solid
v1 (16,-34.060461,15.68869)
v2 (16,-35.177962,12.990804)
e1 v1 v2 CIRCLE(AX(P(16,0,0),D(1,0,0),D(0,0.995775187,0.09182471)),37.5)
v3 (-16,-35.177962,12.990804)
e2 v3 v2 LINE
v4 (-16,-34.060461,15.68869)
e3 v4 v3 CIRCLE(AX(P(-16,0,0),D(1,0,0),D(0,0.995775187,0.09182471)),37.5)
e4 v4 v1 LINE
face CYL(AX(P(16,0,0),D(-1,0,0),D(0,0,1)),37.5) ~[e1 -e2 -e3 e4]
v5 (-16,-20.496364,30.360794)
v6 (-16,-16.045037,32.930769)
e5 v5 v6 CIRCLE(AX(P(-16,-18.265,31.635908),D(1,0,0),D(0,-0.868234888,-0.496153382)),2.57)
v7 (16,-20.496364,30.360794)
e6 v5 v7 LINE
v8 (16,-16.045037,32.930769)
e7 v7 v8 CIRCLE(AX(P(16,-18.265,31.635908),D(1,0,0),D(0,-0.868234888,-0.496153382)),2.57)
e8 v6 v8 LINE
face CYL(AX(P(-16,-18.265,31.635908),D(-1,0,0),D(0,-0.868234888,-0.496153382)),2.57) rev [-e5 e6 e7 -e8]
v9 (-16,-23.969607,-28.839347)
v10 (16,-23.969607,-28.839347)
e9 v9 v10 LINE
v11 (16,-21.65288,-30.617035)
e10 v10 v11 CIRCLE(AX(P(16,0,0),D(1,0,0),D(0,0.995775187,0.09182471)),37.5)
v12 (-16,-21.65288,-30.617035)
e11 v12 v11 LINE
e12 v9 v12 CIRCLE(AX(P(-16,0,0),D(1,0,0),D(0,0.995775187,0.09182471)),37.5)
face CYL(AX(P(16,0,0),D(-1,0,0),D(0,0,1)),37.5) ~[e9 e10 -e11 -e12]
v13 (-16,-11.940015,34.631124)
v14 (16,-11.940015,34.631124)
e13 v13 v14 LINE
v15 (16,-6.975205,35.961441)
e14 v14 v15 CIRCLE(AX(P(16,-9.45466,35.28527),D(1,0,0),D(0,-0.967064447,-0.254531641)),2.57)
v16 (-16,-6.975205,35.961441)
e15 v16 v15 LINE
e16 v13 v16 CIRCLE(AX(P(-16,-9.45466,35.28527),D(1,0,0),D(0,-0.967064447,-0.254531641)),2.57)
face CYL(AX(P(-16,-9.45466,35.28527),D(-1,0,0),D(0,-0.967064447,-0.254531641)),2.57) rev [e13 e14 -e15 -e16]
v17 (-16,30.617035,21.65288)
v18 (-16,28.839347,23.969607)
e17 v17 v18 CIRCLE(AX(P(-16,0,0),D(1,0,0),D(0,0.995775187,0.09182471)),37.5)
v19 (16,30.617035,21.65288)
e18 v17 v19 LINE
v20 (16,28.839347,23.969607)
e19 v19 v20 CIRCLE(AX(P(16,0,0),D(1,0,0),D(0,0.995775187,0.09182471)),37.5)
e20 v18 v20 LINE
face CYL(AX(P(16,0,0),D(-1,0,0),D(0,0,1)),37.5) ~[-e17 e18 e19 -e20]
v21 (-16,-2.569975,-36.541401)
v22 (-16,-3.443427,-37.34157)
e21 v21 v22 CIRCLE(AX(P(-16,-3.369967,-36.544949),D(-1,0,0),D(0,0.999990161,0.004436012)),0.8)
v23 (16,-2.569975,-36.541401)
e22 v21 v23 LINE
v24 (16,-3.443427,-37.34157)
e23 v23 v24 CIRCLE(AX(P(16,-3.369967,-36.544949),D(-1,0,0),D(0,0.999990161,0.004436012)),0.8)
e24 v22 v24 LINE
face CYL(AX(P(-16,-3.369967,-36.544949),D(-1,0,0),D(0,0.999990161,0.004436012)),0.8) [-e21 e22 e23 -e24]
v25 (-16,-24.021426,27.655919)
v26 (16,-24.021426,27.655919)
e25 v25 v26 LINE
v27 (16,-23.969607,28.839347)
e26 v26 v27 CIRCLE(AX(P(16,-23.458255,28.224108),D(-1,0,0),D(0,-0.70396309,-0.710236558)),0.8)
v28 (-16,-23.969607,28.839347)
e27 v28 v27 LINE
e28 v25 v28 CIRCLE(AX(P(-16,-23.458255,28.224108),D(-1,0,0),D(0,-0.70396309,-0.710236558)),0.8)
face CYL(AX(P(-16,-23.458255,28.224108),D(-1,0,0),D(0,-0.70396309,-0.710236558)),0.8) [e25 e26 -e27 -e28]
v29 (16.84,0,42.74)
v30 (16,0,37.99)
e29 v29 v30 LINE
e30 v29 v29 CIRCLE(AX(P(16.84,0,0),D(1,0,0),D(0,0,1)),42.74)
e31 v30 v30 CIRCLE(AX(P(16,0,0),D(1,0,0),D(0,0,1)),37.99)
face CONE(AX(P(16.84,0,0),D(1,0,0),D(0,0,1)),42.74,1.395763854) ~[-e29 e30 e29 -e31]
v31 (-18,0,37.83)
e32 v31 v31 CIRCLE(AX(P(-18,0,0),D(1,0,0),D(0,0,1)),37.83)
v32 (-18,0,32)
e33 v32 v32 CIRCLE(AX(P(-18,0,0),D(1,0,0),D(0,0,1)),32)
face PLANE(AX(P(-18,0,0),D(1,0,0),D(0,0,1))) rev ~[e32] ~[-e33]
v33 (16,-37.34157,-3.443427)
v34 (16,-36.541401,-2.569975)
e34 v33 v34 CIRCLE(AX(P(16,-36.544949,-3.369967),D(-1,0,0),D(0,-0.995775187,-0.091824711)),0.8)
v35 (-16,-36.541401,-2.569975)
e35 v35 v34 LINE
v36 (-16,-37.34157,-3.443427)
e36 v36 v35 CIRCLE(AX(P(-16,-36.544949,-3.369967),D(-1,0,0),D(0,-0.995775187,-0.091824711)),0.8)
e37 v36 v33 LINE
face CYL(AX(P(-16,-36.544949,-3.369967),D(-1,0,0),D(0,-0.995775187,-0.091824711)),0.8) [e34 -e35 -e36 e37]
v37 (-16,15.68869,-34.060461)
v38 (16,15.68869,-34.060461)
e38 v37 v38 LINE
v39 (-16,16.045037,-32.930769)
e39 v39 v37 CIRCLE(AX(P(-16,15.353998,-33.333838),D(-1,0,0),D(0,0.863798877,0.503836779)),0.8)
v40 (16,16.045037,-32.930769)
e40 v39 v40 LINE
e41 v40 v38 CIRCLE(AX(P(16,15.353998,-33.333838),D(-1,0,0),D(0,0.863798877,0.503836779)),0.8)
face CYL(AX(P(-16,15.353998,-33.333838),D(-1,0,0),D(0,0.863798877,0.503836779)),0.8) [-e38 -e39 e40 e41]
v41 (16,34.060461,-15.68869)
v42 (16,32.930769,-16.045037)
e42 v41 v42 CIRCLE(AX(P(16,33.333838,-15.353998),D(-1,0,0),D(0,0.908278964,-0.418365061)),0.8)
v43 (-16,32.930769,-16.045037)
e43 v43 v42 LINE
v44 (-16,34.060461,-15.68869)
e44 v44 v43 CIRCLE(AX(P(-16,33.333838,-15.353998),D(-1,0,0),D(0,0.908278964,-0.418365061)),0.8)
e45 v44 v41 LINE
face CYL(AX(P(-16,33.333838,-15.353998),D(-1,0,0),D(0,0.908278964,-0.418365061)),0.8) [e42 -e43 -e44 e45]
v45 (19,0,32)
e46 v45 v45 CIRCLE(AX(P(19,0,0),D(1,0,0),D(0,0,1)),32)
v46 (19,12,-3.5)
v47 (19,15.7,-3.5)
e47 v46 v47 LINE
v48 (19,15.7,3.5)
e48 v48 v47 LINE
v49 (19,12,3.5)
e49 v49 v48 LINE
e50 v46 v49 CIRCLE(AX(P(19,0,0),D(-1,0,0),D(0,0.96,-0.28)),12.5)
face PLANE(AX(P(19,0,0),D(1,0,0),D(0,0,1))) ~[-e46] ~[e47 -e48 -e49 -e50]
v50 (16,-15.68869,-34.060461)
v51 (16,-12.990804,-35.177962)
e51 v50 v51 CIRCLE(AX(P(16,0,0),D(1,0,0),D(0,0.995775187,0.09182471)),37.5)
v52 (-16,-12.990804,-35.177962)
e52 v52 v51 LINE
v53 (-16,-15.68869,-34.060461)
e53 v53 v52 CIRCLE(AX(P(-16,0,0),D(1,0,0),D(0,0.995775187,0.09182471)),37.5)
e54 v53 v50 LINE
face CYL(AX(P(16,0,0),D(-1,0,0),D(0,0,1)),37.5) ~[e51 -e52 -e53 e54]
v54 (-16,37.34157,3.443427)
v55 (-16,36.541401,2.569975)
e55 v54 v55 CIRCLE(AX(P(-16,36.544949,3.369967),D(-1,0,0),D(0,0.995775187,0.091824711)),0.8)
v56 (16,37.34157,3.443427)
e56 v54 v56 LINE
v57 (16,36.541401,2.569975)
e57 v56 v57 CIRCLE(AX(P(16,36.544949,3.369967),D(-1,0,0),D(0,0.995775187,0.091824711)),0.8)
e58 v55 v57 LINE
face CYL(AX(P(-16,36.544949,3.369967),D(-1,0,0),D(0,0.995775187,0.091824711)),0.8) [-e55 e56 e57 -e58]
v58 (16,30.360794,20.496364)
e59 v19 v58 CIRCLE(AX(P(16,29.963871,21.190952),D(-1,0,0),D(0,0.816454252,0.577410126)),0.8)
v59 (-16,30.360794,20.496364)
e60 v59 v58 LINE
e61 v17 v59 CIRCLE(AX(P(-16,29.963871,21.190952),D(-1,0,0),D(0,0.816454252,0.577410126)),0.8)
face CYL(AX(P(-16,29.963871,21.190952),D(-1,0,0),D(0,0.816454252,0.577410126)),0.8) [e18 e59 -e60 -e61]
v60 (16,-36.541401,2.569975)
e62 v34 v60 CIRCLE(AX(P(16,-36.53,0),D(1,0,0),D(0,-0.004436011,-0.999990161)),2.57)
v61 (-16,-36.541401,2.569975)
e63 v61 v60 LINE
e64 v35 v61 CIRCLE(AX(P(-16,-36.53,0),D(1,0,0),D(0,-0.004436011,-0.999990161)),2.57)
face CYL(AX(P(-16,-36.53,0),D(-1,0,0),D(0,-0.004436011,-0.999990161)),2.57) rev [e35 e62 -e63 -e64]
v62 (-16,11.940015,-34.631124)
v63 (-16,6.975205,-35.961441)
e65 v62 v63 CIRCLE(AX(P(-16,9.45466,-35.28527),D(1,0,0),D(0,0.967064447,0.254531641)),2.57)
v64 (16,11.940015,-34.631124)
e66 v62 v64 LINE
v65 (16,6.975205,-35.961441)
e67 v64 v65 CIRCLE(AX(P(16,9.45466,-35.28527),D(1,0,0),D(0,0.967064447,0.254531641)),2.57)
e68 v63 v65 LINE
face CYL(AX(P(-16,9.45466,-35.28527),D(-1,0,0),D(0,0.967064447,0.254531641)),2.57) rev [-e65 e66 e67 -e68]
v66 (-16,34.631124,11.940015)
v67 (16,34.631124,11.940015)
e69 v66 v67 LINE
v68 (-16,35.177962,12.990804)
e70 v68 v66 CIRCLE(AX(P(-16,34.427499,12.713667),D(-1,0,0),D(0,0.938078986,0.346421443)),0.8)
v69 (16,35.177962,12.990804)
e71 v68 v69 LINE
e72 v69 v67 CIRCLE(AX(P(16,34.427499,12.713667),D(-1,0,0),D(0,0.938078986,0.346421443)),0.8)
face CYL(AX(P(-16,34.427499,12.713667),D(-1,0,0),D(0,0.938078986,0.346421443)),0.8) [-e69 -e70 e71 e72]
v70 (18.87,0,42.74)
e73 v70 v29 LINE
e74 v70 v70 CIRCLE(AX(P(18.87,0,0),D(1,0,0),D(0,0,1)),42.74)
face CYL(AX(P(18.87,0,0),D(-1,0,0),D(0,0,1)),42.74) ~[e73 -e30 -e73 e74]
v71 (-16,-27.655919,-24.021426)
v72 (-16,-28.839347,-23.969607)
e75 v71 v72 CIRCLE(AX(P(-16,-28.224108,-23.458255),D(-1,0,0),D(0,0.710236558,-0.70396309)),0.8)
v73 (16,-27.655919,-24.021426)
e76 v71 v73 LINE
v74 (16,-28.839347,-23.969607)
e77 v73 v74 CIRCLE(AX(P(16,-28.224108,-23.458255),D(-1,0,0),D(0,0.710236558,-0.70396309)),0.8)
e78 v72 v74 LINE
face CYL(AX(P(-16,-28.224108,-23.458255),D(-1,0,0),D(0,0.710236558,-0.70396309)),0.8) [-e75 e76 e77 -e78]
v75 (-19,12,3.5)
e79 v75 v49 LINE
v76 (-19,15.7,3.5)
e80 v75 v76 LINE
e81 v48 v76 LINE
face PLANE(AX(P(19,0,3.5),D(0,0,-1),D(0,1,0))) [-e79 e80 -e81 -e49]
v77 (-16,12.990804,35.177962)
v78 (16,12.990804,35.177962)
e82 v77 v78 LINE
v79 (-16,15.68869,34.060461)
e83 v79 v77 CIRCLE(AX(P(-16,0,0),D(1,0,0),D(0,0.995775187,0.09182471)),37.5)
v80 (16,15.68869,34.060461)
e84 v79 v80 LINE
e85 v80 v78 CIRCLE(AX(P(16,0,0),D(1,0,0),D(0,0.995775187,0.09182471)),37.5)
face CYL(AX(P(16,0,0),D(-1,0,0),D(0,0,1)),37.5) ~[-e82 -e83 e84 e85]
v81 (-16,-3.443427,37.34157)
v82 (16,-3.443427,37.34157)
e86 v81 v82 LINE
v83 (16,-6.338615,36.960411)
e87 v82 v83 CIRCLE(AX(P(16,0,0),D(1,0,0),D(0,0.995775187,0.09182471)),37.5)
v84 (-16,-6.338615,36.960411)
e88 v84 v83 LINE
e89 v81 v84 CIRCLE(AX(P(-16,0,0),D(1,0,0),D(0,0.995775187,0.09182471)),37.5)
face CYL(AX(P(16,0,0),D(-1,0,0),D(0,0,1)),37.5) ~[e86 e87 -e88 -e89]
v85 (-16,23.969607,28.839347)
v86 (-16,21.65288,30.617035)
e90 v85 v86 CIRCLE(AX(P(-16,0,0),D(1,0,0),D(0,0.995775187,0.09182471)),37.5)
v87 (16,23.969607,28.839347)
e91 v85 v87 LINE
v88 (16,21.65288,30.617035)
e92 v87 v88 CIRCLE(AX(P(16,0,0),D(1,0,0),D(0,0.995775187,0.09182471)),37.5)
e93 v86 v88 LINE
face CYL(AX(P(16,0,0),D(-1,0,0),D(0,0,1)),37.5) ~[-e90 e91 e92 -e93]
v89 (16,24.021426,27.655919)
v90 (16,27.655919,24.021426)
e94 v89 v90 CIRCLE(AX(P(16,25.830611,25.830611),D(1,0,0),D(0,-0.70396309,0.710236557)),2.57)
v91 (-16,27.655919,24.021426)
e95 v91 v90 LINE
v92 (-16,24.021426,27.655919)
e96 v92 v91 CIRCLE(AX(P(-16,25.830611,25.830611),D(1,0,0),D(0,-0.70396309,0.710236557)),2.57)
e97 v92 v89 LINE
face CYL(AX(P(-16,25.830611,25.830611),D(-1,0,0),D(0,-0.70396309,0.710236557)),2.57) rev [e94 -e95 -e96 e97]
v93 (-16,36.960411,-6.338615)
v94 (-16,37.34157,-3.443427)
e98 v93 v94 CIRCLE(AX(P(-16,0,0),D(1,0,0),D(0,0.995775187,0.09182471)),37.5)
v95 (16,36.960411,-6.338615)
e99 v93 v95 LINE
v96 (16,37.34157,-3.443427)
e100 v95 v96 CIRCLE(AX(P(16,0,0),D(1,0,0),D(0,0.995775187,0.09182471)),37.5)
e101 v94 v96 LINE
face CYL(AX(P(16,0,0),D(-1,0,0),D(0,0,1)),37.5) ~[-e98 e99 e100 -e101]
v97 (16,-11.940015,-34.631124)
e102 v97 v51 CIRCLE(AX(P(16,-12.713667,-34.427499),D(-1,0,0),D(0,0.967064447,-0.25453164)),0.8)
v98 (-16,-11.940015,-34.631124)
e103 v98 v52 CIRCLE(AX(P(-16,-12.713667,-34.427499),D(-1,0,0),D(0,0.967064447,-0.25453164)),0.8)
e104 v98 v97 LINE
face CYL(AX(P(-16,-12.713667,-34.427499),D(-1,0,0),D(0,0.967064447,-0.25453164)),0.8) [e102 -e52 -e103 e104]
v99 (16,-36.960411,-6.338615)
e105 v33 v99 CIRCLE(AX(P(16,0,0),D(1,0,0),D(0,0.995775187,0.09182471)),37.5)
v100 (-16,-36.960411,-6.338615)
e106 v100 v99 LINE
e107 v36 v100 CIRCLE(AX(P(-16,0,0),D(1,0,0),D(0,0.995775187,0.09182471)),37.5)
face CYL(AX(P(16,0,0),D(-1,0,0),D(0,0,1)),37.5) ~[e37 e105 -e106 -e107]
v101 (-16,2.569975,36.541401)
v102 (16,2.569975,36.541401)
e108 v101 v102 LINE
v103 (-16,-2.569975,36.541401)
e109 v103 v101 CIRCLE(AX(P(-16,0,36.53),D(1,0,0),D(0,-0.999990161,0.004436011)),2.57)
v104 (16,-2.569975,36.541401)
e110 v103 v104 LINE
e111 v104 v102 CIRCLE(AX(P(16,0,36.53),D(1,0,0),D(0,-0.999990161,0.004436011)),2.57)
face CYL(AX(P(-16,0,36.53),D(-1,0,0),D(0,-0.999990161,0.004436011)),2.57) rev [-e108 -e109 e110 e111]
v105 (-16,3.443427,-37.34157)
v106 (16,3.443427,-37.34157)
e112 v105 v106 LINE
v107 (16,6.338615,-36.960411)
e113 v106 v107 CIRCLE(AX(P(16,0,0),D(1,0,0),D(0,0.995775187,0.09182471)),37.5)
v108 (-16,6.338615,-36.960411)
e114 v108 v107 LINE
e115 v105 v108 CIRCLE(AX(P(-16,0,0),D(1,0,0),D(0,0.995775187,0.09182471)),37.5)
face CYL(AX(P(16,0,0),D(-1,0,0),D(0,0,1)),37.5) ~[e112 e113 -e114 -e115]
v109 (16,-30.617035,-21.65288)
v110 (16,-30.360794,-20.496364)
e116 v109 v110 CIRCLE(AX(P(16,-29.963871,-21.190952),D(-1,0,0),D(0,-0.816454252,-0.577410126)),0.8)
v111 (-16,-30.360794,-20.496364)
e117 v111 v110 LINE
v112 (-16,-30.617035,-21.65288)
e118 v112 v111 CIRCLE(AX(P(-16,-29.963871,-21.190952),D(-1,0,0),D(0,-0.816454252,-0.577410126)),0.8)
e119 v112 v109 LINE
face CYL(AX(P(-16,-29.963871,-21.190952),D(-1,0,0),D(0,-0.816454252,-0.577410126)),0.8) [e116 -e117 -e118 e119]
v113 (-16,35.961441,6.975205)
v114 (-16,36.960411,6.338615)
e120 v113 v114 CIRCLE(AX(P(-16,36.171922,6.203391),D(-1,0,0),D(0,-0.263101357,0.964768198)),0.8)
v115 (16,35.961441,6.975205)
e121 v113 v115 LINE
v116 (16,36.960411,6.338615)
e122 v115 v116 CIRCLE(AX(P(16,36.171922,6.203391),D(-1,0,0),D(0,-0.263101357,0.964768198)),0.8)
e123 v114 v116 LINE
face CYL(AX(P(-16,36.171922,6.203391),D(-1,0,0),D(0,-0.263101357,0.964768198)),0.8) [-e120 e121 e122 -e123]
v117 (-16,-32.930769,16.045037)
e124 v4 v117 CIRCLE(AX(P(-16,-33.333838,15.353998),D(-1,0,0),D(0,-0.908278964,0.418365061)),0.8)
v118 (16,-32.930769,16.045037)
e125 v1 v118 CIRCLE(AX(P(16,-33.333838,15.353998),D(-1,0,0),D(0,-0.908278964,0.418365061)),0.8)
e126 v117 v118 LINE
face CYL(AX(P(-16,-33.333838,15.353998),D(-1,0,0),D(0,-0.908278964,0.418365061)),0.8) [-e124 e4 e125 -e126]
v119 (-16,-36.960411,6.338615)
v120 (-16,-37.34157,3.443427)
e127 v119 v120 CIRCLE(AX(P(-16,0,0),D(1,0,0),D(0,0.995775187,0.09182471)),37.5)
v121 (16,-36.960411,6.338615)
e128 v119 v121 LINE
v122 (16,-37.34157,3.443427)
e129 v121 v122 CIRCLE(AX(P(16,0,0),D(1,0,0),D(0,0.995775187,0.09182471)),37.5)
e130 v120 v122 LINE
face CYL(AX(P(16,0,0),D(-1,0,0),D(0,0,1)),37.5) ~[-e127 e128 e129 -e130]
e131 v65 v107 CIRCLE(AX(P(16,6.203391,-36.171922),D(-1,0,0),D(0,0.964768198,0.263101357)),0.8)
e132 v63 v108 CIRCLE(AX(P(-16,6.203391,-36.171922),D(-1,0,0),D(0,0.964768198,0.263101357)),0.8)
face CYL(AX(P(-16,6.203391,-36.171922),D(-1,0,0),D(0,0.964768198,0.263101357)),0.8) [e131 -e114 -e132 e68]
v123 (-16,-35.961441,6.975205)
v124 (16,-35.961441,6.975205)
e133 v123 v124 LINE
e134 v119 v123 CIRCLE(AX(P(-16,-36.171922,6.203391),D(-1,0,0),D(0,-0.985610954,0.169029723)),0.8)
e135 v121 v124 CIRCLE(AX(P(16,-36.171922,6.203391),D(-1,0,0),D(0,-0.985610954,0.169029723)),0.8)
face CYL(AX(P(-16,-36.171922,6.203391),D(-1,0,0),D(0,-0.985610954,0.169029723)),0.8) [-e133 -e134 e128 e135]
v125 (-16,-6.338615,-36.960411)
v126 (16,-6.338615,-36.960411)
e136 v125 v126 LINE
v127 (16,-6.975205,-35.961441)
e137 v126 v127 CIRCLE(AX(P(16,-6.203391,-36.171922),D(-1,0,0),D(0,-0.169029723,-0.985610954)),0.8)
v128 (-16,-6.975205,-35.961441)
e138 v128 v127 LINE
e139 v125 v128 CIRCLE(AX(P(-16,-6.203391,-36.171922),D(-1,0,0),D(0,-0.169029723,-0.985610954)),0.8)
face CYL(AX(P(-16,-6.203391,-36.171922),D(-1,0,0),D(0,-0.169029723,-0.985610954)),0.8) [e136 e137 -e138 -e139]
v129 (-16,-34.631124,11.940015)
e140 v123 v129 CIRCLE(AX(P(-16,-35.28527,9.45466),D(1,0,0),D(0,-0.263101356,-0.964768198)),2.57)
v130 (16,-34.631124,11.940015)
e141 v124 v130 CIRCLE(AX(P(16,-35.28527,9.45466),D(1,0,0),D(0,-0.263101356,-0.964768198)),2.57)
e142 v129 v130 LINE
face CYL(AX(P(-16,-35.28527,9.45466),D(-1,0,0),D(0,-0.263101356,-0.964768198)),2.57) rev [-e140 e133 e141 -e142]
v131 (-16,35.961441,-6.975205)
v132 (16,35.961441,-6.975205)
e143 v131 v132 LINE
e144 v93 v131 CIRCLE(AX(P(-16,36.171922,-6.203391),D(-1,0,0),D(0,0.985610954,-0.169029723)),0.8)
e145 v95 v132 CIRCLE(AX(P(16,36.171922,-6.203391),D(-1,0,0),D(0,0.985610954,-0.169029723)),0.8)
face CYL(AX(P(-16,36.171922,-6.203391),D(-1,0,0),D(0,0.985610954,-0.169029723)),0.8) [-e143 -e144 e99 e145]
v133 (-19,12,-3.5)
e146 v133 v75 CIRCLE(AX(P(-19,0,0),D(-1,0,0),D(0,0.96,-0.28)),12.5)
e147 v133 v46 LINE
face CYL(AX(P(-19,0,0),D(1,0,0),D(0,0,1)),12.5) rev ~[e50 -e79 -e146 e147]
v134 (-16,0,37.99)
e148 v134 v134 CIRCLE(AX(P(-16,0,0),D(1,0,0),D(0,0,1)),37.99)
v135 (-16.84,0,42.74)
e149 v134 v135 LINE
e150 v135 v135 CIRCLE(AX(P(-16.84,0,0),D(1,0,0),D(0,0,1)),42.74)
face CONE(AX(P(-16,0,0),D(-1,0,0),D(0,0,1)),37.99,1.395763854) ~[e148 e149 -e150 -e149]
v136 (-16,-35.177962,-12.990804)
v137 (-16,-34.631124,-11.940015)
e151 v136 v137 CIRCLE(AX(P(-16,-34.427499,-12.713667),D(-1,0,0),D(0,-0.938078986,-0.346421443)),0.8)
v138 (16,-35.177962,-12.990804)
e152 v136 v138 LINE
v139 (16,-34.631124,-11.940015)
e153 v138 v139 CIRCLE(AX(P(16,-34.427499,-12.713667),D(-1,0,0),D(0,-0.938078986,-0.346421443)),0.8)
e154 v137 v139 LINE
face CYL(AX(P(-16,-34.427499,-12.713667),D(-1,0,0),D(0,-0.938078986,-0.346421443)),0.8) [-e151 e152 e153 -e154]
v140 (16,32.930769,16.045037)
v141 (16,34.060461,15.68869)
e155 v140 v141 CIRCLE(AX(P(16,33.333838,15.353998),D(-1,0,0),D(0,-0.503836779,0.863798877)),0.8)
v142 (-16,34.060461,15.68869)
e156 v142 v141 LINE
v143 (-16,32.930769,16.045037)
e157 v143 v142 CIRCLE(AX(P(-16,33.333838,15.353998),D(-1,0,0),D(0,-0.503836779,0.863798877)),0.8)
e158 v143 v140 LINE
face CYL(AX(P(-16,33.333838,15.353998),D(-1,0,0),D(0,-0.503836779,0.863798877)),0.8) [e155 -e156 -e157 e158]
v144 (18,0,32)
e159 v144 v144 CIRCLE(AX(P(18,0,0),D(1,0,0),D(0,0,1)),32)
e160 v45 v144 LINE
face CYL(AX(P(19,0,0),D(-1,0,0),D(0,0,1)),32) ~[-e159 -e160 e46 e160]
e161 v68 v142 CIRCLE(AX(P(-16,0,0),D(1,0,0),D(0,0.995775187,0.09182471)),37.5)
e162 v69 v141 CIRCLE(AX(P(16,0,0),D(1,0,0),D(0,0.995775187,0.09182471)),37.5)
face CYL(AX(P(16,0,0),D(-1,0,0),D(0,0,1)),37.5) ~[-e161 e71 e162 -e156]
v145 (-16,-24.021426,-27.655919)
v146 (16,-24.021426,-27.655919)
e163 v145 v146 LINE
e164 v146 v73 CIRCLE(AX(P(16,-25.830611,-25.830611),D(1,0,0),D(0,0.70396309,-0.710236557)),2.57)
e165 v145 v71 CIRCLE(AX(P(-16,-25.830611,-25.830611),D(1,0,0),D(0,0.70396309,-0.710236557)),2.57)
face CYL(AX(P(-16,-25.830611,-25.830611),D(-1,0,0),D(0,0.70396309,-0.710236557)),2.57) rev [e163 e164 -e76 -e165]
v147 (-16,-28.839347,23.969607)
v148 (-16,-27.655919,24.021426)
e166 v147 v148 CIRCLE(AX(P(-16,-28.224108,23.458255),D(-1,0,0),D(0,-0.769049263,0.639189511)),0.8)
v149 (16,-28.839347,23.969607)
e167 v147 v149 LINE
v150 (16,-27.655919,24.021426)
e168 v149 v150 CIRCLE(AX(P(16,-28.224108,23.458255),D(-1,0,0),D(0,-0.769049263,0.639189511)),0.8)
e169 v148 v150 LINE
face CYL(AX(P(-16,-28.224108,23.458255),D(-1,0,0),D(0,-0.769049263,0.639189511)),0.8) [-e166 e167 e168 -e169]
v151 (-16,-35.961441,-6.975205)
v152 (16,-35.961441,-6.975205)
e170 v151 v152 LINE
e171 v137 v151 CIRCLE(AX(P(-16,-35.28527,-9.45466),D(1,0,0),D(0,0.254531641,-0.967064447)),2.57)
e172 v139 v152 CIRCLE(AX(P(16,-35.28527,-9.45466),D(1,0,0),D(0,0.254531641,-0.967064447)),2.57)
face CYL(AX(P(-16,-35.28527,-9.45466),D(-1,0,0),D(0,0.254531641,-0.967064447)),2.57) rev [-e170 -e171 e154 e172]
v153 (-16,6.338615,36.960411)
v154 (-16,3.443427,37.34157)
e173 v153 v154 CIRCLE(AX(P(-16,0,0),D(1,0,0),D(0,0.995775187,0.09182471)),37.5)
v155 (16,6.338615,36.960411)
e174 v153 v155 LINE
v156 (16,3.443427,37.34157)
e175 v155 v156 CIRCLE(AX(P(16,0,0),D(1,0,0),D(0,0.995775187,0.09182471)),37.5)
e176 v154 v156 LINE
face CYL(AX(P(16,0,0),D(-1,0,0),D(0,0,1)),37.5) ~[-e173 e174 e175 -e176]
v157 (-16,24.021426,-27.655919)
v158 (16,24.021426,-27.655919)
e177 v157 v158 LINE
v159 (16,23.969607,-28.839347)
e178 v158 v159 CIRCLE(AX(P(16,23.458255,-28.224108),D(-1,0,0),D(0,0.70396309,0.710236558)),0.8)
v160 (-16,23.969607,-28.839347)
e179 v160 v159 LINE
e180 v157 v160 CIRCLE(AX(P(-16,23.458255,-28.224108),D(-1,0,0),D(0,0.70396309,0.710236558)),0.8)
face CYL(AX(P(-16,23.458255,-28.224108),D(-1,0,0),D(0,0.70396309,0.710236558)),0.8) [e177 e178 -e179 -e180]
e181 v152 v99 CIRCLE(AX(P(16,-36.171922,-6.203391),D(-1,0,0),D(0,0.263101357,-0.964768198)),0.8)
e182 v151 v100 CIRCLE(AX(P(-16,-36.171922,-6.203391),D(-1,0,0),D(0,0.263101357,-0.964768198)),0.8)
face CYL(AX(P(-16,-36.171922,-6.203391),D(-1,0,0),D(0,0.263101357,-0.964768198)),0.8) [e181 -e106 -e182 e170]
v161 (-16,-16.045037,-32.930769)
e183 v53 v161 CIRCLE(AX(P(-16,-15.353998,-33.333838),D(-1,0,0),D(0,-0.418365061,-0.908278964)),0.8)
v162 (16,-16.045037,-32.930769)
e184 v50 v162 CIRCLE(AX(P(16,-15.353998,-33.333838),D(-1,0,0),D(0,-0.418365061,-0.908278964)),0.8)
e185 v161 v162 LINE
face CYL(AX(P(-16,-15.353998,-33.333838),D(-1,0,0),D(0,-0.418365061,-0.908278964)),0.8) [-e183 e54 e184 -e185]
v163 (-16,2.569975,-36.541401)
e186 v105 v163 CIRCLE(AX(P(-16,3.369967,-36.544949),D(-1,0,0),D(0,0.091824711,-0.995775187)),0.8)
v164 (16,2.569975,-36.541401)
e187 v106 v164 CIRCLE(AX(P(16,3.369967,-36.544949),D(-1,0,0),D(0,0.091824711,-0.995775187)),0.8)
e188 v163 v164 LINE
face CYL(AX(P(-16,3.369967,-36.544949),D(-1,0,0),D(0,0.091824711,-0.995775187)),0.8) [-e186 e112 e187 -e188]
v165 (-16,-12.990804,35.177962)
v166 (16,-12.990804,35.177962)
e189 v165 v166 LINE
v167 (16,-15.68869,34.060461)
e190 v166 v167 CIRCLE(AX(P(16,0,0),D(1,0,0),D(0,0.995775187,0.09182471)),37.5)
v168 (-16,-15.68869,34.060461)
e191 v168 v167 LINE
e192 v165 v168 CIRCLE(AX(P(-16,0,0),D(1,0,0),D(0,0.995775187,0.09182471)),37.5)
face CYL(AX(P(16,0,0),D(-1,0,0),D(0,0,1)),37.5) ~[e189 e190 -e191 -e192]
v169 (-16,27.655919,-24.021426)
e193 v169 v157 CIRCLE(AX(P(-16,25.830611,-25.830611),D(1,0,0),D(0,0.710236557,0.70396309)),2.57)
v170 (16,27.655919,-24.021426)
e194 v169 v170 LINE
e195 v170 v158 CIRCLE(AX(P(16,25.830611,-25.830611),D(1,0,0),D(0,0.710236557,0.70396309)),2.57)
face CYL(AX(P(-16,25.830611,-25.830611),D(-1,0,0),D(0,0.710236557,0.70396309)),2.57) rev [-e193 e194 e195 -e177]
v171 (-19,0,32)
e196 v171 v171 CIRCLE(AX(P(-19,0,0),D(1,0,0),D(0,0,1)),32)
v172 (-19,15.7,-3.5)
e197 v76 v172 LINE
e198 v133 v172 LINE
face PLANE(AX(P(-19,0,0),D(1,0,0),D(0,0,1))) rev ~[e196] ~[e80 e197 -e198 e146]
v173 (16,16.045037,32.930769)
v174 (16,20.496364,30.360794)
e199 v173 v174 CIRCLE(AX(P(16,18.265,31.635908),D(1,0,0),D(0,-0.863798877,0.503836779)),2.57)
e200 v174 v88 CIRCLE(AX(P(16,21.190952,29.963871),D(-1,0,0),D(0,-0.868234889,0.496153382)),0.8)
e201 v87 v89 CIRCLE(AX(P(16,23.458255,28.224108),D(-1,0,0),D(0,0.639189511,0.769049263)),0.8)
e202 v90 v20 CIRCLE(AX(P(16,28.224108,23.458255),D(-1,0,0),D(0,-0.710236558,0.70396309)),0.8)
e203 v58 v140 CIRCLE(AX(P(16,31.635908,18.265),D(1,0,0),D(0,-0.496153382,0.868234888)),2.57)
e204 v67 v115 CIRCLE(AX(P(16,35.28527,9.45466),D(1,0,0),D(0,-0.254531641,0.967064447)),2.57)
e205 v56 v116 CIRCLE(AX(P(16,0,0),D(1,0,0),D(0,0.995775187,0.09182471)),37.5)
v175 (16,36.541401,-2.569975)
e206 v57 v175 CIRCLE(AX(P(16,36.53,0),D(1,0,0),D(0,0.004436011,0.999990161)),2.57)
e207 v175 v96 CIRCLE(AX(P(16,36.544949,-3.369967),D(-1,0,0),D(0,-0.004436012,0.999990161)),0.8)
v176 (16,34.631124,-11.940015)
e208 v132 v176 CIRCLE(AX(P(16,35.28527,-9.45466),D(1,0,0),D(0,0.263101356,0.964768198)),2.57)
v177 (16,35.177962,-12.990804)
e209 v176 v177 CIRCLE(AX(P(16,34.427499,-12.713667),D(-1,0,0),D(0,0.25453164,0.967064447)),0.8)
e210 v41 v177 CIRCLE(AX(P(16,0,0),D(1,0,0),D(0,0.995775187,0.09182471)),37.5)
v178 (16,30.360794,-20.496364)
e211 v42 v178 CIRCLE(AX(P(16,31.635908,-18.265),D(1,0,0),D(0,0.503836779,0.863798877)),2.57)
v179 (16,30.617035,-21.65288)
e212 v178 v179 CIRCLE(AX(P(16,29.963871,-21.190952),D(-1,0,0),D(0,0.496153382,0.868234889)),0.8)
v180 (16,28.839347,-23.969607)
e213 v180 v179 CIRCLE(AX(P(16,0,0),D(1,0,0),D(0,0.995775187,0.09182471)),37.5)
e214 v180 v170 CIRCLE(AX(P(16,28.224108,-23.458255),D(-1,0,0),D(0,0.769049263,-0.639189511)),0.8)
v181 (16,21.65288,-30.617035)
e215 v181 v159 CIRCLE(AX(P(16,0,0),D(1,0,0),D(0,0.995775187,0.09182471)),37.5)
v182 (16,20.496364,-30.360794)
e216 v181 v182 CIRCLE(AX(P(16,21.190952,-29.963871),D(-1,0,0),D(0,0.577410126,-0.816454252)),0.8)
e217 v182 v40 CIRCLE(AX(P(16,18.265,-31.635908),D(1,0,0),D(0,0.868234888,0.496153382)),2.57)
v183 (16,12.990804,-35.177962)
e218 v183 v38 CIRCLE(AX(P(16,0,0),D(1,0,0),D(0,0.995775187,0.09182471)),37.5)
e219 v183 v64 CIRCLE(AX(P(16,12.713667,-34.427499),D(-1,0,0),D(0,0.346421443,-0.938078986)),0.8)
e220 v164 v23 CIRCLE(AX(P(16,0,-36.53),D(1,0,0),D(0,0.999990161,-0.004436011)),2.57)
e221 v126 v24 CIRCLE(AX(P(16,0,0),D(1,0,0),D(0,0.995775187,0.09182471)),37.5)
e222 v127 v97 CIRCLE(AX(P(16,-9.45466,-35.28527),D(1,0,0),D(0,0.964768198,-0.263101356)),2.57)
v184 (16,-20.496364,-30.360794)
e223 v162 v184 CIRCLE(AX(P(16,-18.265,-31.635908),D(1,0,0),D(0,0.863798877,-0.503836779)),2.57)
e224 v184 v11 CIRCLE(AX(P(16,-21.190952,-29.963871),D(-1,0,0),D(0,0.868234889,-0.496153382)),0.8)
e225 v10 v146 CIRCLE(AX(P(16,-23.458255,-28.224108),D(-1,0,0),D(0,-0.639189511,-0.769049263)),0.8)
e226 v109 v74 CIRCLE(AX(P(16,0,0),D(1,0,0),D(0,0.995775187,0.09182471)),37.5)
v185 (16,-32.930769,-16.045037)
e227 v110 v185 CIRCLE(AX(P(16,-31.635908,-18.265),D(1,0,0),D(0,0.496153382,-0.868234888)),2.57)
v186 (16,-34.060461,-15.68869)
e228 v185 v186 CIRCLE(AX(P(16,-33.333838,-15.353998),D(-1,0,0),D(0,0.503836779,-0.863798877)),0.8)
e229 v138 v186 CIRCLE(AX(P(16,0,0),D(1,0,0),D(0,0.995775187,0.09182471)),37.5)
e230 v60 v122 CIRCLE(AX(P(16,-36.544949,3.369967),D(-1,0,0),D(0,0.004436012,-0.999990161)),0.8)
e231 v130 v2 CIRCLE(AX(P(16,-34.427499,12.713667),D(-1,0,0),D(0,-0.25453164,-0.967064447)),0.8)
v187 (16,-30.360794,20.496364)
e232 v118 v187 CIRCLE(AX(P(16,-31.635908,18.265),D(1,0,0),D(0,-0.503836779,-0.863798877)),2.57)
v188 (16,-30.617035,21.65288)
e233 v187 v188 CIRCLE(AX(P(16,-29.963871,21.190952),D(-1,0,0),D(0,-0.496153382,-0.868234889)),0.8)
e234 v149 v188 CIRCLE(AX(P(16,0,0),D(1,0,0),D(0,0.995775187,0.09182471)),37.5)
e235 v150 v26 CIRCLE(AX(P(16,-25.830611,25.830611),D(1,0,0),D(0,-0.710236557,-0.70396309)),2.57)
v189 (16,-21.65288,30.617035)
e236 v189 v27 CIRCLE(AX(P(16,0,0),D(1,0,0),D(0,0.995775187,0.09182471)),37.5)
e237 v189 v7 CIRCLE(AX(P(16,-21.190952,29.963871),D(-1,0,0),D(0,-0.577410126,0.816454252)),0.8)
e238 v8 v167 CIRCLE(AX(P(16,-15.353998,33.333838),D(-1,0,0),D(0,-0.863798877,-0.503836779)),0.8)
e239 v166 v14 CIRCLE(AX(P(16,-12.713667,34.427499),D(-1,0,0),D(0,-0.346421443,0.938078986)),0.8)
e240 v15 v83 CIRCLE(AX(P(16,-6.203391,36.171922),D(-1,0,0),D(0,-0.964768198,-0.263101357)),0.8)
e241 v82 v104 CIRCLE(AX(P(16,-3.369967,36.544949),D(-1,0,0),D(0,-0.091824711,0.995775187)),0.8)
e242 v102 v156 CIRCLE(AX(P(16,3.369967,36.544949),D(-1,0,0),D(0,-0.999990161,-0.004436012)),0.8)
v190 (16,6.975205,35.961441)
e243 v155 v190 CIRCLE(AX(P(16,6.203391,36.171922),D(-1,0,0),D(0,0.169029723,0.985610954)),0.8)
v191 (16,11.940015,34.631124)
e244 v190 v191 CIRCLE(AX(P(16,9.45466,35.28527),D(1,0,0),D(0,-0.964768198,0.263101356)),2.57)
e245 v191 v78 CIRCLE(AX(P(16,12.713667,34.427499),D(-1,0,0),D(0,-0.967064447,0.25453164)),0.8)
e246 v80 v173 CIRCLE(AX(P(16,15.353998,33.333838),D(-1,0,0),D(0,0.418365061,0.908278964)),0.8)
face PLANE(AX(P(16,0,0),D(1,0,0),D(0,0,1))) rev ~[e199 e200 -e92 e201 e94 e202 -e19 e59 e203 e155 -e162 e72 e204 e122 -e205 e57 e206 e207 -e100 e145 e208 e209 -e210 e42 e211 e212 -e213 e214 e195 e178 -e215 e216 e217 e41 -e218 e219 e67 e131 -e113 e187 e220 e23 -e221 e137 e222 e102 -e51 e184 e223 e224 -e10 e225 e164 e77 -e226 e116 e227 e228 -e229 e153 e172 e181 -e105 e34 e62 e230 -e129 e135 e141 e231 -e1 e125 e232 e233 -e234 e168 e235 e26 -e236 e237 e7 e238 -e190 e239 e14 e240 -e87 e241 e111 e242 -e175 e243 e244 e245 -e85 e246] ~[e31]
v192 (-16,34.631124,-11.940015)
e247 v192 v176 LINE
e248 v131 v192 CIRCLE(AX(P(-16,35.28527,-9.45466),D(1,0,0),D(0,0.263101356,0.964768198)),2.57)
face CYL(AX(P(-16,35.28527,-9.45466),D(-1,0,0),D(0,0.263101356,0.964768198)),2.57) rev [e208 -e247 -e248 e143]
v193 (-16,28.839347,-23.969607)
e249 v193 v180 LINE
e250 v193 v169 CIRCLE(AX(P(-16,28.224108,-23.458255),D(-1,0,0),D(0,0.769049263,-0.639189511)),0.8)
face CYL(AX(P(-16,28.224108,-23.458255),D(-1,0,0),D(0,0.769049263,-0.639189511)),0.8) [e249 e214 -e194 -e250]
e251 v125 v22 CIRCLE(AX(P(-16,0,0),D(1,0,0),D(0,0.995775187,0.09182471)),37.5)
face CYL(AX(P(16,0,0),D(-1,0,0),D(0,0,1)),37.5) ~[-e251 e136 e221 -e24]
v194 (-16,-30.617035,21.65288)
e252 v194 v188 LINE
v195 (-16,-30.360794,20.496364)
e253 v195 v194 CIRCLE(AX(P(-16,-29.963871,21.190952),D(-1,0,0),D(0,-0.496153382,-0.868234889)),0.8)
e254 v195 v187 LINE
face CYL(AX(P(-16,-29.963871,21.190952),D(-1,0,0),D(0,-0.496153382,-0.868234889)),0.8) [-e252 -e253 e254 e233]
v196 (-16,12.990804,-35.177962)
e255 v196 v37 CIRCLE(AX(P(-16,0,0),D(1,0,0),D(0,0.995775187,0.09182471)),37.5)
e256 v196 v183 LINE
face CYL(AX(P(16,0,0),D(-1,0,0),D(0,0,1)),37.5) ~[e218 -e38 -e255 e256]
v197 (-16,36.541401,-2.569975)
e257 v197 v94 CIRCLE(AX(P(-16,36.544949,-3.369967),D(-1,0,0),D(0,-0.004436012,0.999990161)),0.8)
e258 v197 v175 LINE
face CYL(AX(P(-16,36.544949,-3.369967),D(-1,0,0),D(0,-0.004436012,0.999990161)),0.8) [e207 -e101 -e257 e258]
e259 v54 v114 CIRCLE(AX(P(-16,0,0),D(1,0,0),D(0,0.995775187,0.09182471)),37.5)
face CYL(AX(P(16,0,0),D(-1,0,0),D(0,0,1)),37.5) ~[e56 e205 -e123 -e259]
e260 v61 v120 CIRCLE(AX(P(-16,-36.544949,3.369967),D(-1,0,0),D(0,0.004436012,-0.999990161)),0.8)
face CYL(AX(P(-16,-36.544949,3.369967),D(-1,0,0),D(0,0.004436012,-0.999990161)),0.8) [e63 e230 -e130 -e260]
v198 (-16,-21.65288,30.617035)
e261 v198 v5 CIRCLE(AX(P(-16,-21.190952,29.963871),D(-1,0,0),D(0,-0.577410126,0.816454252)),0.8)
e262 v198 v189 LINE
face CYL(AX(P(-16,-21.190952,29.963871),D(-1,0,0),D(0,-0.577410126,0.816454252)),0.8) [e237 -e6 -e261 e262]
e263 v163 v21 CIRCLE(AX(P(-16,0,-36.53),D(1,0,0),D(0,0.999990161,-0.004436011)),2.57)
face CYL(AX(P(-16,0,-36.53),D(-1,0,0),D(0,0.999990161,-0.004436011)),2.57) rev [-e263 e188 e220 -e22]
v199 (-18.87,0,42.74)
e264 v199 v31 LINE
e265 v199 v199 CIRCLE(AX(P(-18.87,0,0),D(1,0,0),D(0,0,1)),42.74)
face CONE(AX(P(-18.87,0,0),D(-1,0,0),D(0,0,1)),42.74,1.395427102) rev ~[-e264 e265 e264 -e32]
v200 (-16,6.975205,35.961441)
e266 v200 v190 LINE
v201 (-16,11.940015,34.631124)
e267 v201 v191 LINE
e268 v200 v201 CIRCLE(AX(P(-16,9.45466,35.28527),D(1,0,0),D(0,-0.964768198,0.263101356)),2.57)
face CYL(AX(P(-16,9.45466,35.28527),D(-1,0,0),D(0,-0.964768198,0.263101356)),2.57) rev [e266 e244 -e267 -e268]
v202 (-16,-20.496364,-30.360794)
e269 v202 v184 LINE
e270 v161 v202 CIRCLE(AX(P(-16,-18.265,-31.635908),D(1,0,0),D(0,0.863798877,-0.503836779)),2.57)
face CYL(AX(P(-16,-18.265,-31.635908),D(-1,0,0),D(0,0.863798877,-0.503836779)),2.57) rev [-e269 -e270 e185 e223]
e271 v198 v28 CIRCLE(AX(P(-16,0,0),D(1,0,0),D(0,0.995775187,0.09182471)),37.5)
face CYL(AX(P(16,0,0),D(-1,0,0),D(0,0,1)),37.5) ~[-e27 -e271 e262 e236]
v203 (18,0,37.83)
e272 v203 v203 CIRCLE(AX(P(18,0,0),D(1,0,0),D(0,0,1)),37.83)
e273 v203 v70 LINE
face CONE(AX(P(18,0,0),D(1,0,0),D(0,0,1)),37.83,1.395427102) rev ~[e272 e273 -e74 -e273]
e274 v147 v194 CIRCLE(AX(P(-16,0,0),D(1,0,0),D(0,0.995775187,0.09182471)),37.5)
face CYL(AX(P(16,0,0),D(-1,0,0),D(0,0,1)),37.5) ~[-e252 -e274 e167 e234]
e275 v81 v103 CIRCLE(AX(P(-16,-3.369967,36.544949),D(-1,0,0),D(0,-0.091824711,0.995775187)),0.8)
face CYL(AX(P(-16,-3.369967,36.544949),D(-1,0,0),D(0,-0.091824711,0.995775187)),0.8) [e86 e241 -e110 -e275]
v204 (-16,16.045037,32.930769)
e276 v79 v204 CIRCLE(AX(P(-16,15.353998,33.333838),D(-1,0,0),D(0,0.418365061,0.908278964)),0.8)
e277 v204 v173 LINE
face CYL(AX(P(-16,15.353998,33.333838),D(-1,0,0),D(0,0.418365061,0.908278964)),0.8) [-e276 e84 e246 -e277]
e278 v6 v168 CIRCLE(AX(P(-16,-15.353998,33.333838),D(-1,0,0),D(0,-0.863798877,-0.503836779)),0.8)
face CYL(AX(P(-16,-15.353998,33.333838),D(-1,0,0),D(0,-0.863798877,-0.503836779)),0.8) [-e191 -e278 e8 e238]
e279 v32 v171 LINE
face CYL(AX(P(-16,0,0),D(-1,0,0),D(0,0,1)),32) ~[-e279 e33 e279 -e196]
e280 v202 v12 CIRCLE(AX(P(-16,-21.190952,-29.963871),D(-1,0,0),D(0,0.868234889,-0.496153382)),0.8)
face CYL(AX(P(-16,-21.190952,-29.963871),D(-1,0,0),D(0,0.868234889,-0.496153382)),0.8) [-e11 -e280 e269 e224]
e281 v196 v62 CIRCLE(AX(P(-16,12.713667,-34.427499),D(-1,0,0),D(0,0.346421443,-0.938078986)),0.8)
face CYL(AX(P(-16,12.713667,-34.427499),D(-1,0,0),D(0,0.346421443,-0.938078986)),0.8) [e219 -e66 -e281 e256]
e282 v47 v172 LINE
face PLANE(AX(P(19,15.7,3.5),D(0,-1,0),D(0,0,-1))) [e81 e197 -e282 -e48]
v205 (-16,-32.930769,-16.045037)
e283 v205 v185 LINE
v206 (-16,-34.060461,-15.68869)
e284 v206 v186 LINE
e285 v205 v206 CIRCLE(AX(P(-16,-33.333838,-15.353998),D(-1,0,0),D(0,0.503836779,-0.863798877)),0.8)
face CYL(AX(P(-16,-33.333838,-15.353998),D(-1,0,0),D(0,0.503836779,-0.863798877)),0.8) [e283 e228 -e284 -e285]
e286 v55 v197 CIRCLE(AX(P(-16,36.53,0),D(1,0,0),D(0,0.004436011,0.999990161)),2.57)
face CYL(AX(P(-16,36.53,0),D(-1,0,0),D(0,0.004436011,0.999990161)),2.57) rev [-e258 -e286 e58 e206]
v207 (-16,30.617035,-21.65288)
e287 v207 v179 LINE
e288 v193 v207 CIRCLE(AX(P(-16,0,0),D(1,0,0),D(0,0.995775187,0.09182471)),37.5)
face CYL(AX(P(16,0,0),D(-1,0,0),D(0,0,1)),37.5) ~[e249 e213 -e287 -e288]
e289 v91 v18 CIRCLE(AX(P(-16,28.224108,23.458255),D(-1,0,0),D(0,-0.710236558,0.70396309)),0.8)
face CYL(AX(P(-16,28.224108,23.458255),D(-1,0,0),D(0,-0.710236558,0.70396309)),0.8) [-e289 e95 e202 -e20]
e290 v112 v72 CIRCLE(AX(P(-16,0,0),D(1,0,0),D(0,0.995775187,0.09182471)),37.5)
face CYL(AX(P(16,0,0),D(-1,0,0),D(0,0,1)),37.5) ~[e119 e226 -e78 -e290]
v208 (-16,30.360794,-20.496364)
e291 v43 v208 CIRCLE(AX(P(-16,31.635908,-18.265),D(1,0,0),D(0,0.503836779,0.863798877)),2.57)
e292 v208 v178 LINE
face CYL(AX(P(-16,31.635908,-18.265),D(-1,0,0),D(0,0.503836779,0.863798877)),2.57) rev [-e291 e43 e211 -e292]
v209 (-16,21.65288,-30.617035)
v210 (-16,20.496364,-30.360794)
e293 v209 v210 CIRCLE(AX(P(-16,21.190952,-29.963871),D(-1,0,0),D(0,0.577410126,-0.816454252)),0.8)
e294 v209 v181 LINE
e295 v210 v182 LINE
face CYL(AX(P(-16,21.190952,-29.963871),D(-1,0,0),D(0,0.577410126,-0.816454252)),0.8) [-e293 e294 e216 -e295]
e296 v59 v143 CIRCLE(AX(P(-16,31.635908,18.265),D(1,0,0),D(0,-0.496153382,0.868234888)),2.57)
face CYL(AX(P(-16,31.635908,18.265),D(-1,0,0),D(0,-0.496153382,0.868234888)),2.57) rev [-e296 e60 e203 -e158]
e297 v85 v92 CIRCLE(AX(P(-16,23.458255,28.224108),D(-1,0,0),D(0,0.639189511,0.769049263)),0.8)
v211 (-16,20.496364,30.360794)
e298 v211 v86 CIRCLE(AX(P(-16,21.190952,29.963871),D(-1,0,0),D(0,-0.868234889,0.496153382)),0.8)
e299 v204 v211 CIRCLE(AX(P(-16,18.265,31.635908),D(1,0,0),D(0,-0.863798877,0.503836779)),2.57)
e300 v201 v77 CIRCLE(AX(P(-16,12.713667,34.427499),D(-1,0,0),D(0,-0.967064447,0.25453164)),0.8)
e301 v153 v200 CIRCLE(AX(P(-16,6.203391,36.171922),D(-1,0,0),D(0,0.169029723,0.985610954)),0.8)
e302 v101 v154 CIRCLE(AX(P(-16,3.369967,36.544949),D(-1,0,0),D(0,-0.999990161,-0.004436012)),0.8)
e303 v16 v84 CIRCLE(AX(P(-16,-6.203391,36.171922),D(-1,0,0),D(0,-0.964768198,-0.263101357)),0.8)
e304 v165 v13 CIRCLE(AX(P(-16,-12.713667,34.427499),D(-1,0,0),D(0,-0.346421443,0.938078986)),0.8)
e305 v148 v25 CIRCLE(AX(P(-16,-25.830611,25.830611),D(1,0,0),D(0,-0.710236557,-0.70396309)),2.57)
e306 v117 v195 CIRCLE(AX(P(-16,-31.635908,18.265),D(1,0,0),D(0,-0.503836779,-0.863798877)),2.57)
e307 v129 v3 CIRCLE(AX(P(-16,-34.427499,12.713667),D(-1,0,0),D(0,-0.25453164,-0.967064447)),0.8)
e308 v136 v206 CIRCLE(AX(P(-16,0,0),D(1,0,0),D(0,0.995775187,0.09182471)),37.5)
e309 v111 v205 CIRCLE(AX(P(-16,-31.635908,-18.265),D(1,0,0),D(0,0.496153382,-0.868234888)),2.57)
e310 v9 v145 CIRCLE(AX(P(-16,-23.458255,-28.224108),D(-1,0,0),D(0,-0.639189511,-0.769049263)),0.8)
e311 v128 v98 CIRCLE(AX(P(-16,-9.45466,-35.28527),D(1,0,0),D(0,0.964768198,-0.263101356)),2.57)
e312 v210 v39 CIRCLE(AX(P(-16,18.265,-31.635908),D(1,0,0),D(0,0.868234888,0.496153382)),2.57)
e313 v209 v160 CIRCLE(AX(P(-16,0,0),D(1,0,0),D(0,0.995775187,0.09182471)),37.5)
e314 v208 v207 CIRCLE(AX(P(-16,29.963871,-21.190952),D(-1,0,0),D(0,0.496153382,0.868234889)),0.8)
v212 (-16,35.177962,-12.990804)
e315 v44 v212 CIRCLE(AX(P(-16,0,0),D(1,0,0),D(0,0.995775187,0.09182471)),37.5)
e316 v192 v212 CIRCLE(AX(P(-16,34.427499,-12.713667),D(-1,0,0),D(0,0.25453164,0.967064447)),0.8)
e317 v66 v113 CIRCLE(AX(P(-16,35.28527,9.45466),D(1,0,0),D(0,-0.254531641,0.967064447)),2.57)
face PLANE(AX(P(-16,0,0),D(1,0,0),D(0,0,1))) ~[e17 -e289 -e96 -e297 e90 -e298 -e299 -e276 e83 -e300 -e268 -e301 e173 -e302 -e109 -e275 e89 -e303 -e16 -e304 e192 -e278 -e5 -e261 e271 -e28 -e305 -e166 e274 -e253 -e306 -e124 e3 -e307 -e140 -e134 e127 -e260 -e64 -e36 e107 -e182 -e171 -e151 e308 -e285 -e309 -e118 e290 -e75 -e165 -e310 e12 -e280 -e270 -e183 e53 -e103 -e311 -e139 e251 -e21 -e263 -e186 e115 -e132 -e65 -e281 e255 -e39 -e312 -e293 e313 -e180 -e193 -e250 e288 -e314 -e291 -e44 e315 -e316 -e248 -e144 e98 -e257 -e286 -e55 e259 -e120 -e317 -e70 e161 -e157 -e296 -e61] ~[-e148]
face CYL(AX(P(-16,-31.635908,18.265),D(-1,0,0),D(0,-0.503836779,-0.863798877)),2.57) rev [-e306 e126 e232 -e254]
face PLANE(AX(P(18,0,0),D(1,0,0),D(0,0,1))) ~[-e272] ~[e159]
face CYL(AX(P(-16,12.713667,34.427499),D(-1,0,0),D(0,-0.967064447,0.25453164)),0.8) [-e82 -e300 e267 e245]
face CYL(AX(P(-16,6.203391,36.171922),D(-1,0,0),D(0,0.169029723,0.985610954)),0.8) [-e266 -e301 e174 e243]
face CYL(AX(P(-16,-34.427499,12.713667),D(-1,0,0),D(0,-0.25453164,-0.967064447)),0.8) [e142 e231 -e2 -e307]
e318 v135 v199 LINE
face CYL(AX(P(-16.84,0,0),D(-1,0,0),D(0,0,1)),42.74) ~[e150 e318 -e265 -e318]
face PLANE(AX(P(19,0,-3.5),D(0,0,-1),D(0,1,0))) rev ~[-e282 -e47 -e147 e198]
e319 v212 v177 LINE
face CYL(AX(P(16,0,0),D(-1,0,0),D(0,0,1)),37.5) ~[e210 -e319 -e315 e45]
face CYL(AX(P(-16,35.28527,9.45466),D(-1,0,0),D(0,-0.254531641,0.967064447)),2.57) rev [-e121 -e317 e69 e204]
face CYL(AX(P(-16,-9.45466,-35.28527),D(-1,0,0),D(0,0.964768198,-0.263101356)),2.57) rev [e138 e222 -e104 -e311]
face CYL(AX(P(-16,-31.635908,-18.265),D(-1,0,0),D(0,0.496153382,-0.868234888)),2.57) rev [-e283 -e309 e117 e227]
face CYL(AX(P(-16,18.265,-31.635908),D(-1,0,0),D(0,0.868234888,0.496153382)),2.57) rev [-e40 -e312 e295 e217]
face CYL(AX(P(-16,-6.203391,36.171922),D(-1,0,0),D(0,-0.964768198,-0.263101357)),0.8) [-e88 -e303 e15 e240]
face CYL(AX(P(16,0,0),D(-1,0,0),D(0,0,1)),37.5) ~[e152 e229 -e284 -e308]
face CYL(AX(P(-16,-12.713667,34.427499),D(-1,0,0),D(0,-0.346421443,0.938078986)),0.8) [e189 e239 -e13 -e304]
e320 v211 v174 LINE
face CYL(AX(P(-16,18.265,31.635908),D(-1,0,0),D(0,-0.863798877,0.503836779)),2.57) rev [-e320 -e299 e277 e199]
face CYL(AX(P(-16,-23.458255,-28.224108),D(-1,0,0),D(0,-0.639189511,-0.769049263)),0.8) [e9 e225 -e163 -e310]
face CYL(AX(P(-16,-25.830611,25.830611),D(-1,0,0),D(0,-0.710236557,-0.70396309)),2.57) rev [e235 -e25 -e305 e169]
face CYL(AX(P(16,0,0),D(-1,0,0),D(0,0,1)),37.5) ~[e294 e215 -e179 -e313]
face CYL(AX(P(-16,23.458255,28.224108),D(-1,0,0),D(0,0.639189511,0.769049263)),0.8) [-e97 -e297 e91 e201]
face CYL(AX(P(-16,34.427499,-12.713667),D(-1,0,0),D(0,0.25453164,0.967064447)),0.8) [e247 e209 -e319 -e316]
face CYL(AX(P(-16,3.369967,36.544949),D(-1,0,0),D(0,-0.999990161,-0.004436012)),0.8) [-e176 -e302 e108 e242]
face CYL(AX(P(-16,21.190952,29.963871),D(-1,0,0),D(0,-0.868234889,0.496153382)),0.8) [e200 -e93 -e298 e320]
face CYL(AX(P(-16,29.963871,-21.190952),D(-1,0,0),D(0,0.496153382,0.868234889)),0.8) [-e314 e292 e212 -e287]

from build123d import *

# Parameters (mm, degrees)
SKETCH_2_W               = 7
SKETCH_2_H               = 15.7
CUT_EXTRUDE_1_DEPTH      = 72.396184772
CUT_EXTRUDE_START        = -32
CUT_EXTRUDE_2_DEPTH      = 32
PATTERN_CIRCULAR_1_COUNT = 24


with BuildPart() as part:
    # 草图1 → 旋转1 (revolve)
    with BuildSketch(Plane.XY, mode=Mode.PRIVATE) as revolve_1_sk:
        Polygon((19, 32), (18.87, 32), (18, 32), (16, 32), (16, 37.5), (-16, 37.5), (-16, 32), (-18, 32), (-18.87, 32), (-19, 32), (-19, 12.5), (19, 12.5), align=None)
        Polygon((-16, 32), (-16, 37.5), (-16, 37.99), (-16.84, 42.74), (-18.87, 42.74), (-18, 37.83), (-18, 32), align=None)
        Polygon((18, 37.83), (18.87, 42.74), (16.84, 42.74), (16, 37.99), (16, 37.5), (16, 32), (18, 32), align=None)
    revolve(revolve_1_sk.sketch.rotate(Axis((-24.150544069, 0, 0), (1, 0, 0)), 90), axis=Axis((-24.150544069, 0, 0), (1, 0, 0)))

    # 草图2 → 切除-拉伸1 (cut, through all)
    with BuildSketch(Plane(origin=(19, 0, 0), x_dir=(0, 0, -1), z_dir=(1, 0, 0))):
        with Locations((0, 7.85)):
            Rectangle(SKETCH_2_W, SKETCH_2_H)
    extrude(amount=-CUT_EXTRUDE_1_DEPTH, mode=Mode.SUBTRACT)

    # 草图4 → 切除-拉伸2 (cut)
    with BuildSketch(Plane(origin=(16, 0, 0), x_dir=(0, 0, -1), z_dir=(1, 0, 0)).offset(CUT_EXTRUDE_START)):
        with BuildLine():
            ThreePointArc((3.44342661, 37.341569506), (0, 37.5), (-3.44342661, 37.341569506))
            ThreePointArc((-3.44342661, 37.341569506), (-2.829568925, 37.134839255), (-2.569974713, 36.541400548))
            ThreePointArc((-2.569974713, 36.541400548), (0, 33.96), (2.569974713, 36.541400548))
            ThreePointArc((2.569974713, 36.541400548), (2.829568925, 37.134839255), (3.44342661, 37.341569506))
        make_face()
    cut_extrude_2 = extrude(amount=CUT_EXTRUDE_2_DEPTH, mode=Mode.SUBTRACT)

    # 阵列(圆周)1: 切除-拉伸2 ×24 about axis
    pattern_circular_1_axis = Axis((0, 0, 0), (1, 0, 0))
    for i in range(1, PATTERN_CIRCULAR_1_COUNT):
        add(cut_extrude_2.rotate(pattern_circular_1_axis, i * 360 / PATTERN_CIRCULAR_1_COUNT), mode=Mode.SUBTRACT)


solid = part.part
